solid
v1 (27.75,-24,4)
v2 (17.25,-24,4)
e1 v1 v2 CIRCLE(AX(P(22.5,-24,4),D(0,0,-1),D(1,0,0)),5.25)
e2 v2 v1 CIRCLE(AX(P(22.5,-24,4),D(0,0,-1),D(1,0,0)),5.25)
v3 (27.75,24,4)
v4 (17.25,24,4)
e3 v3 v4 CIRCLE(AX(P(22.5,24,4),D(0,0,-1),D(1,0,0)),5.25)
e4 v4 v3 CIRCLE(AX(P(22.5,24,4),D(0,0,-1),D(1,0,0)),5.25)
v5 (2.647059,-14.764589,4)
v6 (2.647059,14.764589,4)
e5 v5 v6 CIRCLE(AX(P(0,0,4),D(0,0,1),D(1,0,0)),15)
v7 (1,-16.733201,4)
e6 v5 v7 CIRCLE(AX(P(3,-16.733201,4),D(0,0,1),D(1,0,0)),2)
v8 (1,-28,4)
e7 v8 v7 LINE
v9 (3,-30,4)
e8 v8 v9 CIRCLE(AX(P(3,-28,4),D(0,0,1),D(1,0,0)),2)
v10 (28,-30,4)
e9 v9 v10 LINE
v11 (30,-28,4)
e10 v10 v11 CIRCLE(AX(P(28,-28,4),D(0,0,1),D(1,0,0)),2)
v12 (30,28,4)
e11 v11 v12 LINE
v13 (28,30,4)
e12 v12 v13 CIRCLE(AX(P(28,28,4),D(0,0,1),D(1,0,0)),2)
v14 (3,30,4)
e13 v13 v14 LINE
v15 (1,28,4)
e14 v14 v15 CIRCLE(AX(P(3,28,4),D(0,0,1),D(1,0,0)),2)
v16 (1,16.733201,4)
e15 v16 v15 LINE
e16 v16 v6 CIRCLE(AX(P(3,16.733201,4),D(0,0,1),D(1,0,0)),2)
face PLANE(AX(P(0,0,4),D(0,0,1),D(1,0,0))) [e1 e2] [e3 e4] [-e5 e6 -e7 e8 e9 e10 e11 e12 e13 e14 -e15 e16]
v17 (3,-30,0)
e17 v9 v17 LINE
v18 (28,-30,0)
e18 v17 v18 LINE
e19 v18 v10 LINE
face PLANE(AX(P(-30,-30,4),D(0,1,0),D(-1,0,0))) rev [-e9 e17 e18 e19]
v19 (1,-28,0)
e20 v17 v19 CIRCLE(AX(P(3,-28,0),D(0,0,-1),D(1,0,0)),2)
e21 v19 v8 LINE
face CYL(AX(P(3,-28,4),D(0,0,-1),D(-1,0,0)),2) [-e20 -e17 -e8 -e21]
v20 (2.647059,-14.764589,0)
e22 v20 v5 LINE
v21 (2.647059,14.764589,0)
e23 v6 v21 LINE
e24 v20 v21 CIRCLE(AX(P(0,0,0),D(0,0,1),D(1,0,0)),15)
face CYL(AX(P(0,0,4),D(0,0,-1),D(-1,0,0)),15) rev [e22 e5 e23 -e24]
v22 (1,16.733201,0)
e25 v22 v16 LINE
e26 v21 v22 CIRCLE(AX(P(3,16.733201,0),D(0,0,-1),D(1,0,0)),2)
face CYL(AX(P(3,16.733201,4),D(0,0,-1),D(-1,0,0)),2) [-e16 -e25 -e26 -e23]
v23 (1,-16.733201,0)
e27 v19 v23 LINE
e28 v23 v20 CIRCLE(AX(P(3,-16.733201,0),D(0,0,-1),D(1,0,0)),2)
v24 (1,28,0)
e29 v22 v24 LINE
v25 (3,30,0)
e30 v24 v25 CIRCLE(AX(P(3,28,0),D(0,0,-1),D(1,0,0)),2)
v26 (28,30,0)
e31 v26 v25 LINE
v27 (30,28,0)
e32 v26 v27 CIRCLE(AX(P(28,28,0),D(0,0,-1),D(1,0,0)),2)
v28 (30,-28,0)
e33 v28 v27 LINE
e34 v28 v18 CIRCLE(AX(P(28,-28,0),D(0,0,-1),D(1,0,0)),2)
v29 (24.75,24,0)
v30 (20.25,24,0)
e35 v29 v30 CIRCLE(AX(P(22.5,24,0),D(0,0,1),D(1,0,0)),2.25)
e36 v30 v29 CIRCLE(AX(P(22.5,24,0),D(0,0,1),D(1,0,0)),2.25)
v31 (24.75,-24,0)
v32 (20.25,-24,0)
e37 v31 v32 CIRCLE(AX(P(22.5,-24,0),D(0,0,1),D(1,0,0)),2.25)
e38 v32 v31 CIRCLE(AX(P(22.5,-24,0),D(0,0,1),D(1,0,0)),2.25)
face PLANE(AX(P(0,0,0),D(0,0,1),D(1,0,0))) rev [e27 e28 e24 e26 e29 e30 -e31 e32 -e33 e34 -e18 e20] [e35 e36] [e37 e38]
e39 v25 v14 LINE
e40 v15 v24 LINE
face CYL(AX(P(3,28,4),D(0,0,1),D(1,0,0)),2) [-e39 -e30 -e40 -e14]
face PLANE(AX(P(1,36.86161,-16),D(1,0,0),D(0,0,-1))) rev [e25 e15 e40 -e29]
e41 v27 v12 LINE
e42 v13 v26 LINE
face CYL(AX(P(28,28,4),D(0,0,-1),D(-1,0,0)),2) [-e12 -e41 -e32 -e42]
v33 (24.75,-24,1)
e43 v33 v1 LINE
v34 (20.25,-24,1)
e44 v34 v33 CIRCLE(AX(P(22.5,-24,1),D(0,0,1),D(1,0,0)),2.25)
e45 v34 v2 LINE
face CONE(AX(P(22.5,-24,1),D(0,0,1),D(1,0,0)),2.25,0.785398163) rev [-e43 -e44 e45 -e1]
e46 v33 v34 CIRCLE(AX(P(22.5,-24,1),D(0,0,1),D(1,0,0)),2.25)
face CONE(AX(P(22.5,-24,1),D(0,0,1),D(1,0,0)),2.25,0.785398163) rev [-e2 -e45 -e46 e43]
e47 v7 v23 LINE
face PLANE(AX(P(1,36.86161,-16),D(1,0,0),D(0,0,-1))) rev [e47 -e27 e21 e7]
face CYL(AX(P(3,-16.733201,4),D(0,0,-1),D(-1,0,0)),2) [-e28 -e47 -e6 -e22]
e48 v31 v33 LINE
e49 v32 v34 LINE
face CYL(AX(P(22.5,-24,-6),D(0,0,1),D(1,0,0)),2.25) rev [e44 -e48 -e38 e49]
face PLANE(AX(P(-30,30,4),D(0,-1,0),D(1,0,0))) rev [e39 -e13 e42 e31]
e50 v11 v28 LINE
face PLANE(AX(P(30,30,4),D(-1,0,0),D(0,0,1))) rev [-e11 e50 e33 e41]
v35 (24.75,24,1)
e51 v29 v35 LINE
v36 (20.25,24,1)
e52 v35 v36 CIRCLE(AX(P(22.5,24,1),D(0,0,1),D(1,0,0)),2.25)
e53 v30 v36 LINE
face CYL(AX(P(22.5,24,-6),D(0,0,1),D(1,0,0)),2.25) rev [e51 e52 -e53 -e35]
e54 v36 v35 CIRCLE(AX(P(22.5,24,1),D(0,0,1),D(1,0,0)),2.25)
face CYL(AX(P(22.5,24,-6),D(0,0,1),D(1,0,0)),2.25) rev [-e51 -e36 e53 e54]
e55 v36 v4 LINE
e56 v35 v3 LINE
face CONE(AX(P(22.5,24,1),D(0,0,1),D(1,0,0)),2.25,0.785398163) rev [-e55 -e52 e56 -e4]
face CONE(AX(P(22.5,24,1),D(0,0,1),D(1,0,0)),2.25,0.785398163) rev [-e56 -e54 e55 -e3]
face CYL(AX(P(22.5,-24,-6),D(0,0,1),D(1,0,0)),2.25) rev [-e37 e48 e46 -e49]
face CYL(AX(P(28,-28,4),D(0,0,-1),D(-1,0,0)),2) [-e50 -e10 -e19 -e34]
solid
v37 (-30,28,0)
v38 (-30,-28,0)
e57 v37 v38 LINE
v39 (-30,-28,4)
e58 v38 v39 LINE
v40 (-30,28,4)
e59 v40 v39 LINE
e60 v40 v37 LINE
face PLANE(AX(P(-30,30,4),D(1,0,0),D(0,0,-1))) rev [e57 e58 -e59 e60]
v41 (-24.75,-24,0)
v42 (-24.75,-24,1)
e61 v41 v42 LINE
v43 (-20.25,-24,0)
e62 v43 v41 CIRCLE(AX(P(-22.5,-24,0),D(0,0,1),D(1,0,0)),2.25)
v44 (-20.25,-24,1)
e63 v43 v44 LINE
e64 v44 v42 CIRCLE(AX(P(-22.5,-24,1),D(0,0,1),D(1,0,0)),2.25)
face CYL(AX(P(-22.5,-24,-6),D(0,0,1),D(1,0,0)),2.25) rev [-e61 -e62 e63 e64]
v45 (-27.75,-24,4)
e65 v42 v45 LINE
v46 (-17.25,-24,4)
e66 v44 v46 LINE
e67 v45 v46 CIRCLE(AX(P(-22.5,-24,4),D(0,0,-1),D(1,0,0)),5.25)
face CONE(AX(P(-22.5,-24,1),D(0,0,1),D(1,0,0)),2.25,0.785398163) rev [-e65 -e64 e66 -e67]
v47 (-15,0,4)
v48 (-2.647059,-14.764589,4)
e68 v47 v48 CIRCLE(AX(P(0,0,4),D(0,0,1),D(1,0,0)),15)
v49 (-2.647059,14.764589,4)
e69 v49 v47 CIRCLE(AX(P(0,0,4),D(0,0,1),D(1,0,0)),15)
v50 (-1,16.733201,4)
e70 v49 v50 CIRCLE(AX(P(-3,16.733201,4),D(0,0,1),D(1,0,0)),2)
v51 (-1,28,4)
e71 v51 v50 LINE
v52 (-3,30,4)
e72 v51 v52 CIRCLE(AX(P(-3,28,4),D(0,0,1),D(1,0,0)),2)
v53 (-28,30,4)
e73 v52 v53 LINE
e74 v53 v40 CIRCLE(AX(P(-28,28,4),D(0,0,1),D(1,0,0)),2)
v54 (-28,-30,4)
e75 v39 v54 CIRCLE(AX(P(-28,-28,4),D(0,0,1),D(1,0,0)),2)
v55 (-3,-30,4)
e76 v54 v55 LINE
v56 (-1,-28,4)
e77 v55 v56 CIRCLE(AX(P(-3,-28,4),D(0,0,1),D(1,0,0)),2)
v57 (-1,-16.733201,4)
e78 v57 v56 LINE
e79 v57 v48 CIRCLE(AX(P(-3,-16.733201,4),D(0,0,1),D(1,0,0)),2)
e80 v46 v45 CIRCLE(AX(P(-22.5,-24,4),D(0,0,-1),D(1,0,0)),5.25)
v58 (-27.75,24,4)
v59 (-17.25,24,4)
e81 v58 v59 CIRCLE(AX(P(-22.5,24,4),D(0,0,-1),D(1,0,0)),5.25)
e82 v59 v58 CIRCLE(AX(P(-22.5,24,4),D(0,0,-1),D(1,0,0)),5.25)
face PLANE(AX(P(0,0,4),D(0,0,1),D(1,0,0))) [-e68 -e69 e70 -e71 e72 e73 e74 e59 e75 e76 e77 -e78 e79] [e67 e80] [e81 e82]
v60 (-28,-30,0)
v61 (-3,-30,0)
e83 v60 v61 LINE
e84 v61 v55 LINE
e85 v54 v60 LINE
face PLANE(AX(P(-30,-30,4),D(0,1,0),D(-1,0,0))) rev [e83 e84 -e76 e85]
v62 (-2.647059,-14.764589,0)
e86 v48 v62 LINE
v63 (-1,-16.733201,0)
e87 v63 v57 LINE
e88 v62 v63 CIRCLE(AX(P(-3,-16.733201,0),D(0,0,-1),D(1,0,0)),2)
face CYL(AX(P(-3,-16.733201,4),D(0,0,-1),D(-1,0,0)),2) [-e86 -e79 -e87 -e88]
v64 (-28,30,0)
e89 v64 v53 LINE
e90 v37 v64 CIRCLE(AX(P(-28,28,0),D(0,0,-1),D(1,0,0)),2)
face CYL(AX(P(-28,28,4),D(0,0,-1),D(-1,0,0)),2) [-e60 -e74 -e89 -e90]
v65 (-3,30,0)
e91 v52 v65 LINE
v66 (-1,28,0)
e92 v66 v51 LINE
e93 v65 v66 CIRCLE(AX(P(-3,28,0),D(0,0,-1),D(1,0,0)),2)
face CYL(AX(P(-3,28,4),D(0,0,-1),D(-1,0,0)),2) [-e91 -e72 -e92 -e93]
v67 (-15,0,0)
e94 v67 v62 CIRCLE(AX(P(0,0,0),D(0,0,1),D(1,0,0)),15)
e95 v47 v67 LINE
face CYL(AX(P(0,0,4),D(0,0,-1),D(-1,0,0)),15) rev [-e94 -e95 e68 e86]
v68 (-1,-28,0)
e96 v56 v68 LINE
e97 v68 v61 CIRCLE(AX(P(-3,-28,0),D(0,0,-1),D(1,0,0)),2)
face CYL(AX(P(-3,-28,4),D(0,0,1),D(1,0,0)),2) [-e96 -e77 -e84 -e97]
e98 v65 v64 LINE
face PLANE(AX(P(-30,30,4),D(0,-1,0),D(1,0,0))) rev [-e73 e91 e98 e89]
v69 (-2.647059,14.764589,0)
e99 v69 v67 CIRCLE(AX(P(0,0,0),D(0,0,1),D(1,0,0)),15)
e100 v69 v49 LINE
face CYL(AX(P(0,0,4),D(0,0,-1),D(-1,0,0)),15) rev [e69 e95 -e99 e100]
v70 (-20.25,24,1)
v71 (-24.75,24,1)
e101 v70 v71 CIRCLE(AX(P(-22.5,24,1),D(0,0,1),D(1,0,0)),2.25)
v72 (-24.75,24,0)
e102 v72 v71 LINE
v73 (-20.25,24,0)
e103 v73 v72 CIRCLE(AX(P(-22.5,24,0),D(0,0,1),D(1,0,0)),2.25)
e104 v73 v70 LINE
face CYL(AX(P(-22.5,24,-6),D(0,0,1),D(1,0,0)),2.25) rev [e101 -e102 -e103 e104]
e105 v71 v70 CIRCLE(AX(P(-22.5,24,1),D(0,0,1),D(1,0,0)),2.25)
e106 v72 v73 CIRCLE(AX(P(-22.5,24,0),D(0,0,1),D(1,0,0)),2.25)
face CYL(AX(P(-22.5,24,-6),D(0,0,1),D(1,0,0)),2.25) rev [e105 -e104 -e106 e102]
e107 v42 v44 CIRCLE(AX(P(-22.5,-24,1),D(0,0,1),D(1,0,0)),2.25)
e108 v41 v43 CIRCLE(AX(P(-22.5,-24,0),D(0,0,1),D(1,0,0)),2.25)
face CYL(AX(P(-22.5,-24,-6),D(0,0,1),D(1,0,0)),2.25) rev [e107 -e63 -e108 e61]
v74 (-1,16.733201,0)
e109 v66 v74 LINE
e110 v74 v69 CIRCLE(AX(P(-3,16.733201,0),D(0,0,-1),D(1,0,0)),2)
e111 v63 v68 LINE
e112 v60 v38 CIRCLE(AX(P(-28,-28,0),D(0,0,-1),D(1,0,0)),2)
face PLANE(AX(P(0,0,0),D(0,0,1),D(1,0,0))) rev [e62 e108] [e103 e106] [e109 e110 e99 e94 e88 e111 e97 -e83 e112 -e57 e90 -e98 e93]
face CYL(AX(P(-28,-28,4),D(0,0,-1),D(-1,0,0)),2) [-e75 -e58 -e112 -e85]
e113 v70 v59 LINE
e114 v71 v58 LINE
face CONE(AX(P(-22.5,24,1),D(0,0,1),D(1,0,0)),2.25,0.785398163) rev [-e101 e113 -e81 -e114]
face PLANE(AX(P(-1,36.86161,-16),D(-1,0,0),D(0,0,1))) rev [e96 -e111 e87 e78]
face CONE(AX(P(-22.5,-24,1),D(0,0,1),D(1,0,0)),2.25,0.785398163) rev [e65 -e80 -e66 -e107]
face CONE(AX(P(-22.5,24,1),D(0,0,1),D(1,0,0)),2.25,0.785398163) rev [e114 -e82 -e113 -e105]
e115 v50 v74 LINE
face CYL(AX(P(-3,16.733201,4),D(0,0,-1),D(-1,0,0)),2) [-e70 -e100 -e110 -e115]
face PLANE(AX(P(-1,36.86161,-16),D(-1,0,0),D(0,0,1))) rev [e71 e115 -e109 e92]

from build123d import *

# Parameters (mm, degrees)
SKETCH_1_W          = 60
SKETCH_1_H          = 60
SKETCH_1_R          = 15
EXTRUDE_1_DEPTH     = 4
SKETCH_2_W          = 2
SKETCH_2_H          = 73.723220536
CUT_EXTRUDE_1_DEPTH = 20
SKETCH_3_R          = 2.25
CUT_EXTRUDE_2_DEPTH = 10
CHAMFER_1_SIZE      = 3
CHAMFER_2_SIZE      = 3
FILLET_1_R          = 2
FILLET_2_R          = 2


with BuildPart() as part:
    # 草图1 → 凸台-拉伸1 (new body)
    with BuildSketch(Plane.XY):
        Rectangle(SKETCH_1_W, SKETCH_1_H)
        Circle(SKETCH_1_R, mode=Mode.SUBTRACT)
    extrude(amount=EXTRUDE_1_DEPTH)

    # 草图2 → 切除-拉伸1 (cut)
    with BuildSketch(Plane.XY.offset(4)):
        Rectangle(SKETCH_2_W, SKETCH_2_H)
    extrude(amount=-CUT_EXTRUDE_1_DEPTH, mode=Mode.SUBTRACT)


with BuildPart() as cut_extrude_1_piece_1:
    # of the separate pieces the step leaves, piece 1, a body of its own (cut_extrude_1_pieces)
    add(part.part.solids().sort_by_distance((-30, 30, 0))[0])


with BuildPart() as cut_extrude_1_piece_2:
    # of the separate pieces the step leaves, piece 2, a body of its own (cut_extrude_1_pieces)
    add(part.part.solids().sort_by_distance((1, 30, 0))[0])


with BuildPart() as cut_extrude_2_tool:
    # 草图3 → 切除-拉伸2 (new body)
    with BuildSketch(Plane.XY.offset(4)):
        with Locations((-22.5, 24)):
            Circle(SKETCH_3_R)
        with Locations((22.5, 24)):
            Circle(SKETCH_3_R)
        with Locations((-22.5, -24)):
            Circle(SKETCH_3_R)
        with Locations((22.5, -24)):
            Circle(SKETCH_3_R)
    extrude(amount=-CUT_EXTRUDE_2_DEPTH)


with BuildPart() as cut_extrude_1_piece_1_1:
    add(cut_extrude_1_piece_1.part)

    # 切除-拉伸2: cut by cut_extrude_2_tool
    add(cut_extrude_2_tool.part, mode=Mode.SUBTRACT)

    # 倒角1
    chamfer_1_edges = [cut_extrude_1_piece_1_1.edges().sort_by_distance(p)[0] for p in [
        (-24.75, 24, 4),
        (-24.75, -24, 4),
    ]]
    chamfer(chamfer_1_edges, length=CHAMFER_1_SIZE)

    # 圆角2
    fillet_2_edges = [cut_extrude_1_piece_1_1.edges().sort_by_distance(p)[0] for p in [
        (-1, -14.966629547, 2),
        (-1, 14.966629547, 2),
        (-1, 30, 2),
        (-1, -30, 2),
        (-30, -30, 2),
        (-30, 30, 2),
    ]]
    fillet(fillet_2_edges, radius=FILLET_2_R)


with BuildPart() as cut_extrude_1_piece_2_1:
    add(cut_extrude_1_piece_2.part)

    # 切除-拉伸2: cut by cut_extrude_2_tool
    add(cut_extrude_2_tool.part, mode=Mode.SUBTRACT)

    # 倒角2
    chamfer_2_edges = [cut_extrude_1_piece_2_1.edges().sort_by_distance(p)[0] for p in [
        (20.25, 24, 4),
        (20.25, -24, 4),
    ]]
    chamfer(chamfer_2_edges, length=CHAMFER_2_SIZE)

    # 圆角1
    fillet_1_edges = [cut_extrude_1_piece_2_1.edges().sort_by_distance(p)[0] for p in [
        (1, 30, 2),
        (30, 30, 2),
        (1, -30, 2),
        (30, -30, 2),
        (1, 14.966629547, 2),
        (1, -14.966629547, 2),
    ]]
    fillet(fillet_1_edges, radius=FILLET_1_R)


solid = Compound([cut_extrude_1_piece_1_1.part, cut_extrude_1_piece_2_1.part])
